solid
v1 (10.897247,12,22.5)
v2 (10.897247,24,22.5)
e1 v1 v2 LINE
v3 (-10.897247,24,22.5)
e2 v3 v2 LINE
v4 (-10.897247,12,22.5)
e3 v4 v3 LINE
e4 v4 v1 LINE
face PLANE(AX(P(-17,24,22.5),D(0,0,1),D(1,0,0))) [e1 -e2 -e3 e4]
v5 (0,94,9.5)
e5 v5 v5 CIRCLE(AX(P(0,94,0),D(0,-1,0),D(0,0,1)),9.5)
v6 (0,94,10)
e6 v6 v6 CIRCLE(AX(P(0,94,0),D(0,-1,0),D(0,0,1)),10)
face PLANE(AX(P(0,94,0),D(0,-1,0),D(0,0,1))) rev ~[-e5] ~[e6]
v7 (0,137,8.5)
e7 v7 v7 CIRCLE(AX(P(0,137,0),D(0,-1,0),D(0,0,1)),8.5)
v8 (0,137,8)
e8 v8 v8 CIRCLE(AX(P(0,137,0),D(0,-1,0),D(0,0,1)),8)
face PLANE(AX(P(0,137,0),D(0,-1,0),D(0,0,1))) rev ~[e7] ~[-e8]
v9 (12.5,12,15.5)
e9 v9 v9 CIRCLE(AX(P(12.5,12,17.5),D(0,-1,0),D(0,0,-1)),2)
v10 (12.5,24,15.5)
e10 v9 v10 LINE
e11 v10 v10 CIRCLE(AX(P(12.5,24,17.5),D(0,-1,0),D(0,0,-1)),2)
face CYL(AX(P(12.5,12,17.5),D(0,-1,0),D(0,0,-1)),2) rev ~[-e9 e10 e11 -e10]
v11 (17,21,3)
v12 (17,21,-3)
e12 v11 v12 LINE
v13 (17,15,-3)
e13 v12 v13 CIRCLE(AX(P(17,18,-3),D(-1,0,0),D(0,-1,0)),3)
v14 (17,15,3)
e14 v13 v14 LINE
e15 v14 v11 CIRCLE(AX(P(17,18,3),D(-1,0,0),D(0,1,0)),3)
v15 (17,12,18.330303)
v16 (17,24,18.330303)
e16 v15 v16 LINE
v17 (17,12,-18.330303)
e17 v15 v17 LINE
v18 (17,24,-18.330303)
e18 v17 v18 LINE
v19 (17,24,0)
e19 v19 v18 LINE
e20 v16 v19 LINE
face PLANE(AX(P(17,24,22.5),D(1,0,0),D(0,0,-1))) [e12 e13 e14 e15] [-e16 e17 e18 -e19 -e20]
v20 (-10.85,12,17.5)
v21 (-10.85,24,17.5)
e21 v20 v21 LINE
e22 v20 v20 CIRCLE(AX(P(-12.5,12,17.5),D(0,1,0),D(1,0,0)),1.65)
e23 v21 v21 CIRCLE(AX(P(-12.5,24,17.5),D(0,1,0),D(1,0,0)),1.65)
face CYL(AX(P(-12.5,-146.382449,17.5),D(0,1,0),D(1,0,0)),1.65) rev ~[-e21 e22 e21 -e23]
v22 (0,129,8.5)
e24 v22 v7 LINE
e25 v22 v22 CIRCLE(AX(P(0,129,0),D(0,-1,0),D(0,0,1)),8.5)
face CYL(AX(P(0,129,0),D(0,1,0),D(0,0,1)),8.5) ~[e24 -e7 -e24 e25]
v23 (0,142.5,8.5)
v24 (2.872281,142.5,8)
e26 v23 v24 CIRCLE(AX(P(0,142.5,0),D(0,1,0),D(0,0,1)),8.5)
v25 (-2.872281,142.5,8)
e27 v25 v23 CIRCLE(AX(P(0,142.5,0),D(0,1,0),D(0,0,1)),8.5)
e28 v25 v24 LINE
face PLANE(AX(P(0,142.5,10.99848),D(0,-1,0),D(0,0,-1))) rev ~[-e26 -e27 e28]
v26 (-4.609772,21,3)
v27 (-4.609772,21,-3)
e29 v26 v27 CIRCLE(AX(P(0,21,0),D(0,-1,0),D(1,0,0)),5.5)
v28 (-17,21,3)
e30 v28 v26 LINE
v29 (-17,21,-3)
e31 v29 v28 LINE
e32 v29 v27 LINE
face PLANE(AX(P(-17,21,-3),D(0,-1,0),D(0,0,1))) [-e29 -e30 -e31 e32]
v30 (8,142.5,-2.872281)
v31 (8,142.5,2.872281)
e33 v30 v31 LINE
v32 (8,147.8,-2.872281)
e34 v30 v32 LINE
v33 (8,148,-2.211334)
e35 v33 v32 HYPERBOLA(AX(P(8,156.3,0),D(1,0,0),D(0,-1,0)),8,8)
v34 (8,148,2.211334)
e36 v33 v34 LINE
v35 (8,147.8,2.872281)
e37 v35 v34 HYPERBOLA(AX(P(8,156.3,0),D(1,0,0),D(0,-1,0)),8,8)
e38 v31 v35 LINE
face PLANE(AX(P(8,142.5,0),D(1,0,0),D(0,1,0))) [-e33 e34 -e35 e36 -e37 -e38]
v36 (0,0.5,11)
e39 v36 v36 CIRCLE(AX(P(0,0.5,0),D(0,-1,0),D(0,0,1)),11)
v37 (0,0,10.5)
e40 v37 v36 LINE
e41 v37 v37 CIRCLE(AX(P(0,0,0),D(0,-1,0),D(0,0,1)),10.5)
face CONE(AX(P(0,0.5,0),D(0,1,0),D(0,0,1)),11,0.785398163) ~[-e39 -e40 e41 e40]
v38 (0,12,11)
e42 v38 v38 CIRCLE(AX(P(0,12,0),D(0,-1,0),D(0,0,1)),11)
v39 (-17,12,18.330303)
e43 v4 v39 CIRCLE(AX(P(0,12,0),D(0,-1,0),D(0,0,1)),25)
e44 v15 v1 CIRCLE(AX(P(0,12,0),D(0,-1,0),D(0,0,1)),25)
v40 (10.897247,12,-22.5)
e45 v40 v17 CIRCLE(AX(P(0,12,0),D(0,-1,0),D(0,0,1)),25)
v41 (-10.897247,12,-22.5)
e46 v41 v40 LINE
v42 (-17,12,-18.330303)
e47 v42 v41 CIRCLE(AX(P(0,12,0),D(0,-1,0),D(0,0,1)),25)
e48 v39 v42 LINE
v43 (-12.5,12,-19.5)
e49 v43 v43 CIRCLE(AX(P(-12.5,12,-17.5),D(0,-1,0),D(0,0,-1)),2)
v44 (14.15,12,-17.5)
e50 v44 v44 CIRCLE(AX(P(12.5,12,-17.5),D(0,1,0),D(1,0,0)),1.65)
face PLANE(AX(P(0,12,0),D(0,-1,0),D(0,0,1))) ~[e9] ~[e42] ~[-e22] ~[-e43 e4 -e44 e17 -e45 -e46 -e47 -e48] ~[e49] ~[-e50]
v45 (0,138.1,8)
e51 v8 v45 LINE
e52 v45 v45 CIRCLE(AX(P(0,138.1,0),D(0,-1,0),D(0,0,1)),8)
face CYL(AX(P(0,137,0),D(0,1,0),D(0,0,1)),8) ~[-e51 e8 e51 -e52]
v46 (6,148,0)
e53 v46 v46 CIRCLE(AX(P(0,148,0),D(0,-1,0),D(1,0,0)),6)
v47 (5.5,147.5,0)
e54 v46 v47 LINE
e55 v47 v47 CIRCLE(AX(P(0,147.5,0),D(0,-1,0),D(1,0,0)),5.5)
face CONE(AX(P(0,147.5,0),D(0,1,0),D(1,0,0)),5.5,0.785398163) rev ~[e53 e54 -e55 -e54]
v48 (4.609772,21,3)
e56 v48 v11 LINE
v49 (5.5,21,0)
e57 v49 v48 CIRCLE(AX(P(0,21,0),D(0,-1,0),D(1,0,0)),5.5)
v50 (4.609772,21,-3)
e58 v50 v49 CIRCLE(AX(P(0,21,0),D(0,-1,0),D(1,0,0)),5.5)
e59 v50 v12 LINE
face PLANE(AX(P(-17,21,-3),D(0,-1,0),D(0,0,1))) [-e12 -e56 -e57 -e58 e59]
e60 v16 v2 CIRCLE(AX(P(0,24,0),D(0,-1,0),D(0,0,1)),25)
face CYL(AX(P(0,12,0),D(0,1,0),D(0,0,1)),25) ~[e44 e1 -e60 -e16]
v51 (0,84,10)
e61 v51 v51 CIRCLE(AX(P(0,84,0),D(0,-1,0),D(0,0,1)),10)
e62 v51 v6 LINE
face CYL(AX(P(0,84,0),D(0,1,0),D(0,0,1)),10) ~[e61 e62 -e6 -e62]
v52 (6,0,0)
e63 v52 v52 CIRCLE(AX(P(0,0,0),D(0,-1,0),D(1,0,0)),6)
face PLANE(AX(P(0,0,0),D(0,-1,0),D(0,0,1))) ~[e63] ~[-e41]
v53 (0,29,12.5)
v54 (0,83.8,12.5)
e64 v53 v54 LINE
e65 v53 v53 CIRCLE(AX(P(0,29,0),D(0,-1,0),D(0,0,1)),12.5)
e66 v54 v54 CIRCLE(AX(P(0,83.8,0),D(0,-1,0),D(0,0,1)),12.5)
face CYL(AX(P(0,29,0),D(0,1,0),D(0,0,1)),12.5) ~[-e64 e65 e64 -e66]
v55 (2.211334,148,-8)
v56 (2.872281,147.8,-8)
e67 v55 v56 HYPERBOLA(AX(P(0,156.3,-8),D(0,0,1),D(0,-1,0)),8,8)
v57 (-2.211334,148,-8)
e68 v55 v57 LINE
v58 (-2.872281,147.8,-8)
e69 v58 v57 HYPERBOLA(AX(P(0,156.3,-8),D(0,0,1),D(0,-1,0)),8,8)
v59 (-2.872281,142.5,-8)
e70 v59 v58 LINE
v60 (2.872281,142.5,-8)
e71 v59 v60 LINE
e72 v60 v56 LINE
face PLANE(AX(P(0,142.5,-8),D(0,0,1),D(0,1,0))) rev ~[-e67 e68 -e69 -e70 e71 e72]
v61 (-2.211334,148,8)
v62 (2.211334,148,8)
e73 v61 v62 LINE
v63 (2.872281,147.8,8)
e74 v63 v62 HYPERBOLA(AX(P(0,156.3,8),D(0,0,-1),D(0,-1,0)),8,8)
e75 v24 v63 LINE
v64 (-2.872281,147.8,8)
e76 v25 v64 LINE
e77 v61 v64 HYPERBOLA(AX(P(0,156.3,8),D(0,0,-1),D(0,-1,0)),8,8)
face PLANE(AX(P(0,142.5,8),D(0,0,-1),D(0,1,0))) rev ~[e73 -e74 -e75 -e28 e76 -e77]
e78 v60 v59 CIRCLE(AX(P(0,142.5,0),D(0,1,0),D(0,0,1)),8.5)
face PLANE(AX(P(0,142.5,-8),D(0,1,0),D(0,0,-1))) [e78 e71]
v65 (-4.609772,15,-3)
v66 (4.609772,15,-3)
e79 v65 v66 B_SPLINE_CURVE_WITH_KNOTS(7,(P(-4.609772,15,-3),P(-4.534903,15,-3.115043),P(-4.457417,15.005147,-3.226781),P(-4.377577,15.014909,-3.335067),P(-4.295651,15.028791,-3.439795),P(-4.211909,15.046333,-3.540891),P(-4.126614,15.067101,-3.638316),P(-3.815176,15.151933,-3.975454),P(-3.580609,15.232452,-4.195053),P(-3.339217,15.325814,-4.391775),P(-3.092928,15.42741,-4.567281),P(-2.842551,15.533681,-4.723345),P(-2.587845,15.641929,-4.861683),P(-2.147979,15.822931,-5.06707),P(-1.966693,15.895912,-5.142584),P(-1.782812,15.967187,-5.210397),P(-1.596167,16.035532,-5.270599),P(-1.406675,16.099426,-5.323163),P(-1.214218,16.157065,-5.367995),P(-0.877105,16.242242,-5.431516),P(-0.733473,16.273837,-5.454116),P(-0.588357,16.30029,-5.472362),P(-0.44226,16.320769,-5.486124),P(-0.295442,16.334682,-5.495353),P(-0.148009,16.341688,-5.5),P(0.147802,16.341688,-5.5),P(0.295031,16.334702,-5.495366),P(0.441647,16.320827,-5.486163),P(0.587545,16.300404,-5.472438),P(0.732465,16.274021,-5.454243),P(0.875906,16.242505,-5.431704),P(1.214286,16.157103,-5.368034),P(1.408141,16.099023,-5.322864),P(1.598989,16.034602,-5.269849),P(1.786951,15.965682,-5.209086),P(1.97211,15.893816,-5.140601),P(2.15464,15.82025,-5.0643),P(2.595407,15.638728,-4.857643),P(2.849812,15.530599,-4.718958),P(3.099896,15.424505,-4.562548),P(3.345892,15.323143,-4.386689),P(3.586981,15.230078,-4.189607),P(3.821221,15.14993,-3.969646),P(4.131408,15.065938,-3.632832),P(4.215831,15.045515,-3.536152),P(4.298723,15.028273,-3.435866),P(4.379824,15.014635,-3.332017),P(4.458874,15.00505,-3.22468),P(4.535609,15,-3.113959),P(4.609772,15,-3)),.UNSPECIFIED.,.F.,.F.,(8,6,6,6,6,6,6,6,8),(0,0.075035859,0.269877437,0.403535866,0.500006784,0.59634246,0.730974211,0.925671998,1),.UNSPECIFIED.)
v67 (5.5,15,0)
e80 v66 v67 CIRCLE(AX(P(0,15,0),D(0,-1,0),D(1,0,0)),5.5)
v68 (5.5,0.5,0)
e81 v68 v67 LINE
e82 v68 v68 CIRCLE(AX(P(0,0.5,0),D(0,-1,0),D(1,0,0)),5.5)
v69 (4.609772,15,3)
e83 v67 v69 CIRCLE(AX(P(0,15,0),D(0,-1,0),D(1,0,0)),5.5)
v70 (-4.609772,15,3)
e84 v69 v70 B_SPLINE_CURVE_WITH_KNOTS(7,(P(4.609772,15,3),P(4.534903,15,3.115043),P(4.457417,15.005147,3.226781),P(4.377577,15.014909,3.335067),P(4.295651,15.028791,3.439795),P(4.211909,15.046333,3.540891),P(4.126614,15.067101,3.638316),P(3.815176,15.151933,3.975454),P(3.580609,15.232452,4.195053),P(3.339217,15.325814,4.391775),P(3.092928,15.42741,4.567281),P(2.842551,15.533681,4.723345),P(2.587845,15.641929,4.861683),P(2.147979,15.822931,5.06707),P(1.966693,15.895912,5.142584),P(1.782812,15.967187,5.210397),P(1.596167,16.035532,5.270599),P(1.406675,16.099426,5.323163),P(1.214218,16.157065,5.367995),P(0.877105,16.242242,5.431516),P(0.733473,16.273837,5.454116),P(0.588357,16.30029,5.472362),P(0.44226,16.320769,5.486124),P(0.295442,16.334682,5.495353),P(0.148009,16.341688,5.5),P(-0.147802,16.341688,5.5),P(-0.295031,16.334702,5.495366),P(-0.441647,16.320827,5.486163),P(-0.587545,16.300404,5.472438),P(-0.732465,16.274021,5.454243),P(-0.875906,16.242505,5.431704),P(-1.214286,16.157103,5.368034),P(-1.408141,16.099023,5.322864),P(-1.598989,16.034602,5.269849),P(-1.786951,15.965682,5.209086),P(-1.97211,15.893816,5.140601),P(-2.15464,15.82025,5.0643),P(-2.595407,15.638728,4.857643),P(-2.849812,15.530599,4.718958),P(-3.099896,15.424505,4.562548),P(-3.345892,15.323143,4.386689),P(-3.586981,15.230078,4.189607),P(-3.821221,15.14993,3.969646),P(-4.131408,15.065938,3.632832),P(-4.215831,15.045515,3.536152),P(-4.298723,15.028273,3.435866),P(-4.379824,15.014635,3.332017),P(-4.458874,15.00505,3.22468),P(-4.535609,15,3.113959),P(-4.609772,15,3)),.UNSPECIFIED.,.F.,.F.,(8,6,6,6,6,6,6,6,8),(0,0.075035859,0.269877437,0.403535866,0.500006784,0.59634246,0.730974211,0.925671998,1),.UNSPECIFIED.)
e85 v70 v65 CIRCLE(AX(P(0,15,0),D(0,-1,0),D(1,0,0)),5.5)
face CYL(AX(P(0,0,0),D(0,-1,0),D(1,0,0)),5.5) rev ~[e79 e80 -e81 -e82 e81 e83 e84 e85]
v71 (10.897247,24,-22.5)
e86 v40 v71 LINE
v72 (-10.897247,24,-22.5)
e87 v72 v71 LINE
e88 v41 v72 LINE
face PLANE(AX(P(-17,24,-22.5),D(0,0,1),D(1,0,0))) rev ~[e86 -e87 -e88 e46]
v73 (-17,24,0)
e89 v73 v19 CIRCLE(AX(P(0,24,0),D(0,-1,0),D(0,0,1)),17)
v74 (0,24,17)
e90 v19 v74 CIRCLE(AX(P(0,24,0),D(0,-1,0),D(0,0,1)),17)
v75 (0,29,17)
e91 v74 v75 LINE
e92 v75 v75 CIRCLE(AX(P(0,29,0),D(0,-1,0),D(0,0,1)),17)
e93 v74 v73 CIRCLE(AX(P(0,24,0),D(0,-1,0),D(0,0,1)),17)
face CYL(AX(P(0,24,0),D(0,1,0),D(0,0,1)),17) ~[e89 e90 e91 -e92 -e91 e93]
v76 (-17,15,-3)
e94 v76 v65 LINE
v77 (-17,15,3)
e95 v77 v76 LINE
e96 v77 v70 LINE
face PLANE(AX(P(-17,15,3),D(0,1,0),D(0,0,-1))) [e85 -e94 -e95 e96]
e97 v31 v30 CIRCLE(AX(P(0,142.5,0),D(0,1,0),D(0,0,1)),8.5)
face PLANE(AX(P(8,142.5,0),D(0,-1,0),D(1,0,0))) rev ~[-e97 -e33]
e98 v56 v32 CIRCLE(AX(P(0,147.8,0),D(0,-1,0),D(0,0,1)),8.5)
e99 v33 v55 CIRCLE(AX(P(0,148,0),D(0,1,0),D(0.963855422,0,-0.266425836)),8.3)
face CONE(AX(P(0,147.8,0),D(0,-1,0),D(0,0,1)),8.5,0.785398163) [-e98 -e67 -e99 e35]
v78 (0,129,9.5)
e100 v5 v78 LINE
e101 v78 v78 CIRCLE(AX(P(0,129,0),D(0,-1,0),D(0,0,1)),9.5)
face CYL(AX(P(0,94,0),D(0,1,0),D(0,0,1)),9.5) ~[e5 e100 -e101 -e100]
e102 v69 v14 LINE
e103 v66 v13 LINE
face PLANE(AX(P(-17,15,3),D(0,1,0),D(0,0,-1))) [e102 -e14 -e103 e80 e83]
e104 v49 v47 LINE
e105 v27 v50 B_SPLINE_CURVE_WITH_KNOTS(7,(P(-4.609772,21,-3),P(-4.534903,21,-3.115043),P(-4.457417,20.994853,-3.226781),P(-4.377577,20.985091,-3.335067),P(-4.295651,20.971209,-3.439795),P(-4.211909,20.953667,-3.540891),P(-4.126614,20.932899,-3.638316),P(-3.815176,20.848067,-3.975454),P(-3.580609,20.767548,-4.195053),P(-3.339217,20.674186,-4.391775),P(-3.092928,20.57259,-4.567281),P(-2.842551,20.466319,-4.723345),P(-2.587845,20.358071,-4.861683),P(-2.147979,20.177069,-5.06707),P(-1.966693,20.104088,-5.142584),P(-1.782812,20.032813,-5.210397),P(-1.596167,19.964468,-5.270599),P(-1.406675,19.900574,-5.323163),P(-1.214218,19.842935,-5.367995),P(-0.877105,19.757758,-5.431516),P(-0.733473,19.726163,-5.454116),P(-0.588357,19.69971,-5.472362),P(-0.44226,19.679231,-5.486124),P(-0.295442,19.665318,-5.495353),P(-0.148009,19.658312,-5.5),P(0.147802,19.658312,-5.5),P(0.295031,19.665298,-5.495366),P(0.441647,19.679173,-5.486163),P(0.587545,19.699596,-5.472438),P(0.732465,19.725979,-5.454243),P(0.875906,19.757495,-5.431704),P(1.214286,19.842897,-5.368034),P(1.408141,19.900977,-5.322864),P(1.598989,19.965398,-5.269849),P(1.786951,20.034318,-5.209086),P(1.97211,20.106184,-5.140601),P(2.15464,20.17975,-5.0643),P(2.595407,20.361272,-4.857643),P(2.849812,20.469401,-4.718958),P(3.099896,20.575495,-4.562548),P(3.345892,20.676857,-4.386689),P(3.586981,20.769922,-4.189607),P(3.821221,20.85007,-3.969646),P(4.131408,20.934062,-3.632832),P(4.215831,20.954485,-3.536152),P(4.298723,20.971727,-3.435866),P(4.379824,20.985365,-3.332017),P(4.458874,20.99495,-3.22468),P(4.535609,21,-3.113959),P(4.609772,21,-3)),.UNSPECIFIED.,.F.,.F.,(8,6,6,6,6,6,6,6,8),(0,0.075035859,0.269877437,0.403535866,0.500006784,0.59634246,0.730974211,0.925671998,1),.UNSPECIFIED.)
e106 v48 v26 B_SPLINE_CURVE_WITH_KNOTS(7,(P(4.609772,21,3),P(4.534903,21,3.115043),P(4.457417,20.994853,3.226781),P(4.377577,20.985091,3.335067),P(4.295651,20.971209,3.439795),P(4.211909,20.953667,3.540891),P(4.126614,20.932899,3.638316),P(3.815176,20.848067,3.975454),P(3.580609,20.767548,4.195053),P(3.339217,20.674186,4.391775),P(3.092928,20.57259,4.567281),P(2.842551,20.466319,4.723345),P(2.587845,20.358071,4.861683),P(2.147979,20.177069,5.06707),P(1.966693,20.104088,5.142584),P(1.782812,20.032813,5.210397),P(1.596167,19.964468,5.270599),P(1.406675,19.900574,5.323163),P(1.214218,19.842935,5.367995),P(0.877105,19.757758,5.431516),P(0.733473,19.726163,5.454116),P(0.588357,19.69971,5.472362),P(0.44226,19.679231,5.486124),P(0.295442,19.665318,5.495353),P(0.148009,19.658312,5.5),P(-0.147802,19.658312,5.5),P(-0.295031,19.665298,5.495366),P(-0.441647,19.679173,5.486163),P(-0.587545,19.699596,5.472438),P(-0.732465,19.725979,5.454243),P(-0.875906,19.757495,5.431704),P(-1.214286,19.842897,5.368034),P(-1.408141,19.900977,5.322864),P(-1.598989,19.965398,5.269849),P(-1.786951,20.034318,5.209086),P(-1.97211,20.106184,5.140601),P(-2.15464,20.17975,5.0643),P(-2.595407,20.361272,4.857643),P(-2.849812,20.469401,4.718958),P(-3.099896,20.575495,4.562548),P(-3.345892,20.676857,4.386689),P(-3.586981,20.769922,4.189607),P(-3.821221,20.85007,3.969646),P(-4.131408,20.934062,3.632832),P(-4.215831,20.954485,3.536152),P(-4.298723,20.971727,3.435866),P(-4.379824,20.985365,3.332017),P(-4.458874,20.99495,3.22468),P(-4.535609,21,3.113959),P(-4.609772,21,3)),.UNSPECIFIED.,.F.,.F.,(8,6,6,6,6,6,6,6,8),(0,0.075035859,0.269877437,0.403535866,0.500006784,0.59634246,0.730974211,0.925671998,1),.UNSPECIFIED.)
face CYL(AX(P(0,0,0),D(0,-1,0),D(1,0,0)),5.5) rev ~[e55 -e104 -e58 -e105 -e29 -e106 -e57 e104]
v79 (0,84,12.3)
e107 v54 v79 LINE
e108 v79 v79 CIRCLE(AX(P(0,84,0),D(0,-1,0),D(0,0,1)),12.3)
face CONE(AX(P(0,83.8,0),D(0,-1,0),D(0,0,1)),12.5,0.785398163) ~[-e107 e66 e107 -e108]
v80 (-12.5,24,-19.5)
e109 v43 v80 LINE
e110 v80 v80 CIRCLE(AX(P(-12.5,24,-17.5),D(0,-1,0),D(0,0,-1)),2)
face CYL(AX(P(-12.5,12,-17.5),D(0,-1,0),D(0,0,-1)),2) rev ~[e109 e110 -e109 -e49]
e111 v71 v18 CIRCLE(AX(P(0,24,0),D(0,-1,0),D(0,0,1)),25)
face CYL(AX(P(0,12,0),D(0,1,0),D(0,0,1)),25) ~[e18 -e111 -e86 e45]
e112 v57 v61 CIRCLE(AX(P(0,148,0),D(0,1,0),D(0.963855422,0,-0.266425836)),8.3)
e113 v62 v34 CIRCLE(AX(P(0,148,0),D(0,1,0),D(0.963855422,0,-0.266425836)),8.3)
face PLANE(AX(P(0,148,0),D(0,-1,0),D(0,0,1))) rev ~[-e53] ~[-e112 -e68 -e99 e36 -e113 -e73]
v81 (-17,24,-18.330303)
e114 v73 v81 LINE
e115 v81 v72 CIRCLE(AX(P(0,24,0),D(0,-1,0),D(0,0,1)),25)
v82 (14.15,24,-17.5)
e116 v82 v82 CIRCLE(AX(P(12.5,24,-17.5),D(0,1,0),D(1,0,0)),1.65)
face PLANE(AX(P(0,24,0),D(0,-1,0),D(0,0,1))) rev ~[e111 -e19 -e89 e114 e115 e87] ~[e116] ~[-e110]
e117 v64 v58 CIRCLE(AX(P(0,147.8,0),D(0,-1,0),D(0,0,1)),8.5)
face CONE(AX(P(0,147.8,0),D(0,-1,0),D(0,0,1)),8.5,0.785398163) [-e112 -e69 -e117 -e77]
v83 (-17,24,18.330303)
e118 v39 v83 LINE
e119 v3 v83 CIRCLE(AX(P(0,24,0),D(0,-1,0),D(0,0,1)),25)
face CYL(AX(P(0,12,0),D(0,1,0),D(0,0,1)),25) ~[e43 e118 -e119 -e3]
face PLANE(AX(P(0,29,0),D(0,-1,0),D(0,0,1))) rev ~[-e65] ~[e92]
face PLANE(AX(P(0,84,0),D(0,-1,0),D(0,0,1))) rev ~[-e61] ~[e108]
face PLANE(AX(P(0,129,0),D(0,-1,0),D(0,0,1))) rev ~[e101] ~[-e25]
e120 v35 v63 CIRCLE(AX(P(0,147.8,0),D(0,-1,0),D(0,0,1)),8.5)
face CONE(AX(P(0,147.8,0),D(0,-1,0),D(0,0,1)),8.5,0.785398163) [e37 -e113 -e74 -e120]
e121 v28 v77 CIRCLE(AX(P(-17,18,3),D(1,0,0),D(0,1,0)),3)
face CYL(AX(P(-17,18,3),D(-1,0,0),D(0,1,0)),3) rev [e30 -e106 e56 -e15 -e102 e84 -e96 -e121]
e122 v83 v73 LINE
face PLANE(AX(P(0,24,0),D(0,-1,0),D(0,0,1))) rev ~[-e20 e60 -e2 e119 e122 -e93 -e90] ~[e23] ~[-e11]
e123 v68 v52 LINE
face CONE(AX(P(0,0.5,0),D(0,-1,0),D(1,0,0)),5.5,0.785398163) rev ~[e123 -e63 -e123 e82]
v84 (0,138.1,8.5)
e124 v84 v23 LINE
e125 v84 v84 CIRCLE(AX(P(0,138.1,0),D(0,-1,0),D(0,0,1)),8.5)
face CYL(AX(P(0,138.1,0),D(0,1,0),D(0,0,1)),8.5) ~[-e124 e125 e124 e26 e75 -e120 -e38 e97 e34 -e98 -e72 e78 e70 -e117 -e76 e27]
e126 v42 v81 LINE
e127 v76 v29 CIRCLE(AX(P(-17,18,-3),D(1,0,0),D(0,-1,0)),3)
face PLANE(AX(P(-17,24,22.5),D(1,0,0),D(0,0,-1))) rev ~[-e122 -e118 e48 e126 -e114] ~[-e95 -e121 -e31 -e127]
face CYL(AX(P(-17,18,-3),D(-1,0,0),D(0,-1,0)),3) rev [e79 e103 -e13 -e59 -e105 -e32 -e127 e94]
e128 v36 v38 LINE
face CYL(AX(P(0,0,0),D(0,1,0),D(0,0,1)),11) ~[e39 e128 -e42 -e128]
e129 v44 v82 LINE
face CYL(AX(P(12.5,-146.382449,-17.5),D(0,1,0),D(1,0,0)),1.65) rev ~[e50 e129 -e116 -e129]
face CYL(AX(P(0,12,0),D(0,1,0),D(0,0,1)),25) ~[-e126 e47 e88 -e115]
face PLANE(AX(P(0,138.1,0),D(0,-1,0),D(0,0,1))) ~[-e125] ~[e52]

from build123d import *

# Parameters (mm, degrees)
SKETCH7_OUTSIDE_W   = 84.804
SKETCH7_OUTSIDE_H   = 84.804
SKETCH7_OUTSIDE_W_2 = 34
SKETCH7_OUTSIDE_H_2 = 45
CUT_EXTRUDE3_DEPTH  = 25
M4_TAPPED_HOLE2_D   = 3.3
SKETCH13_R          = 2
CUT_EXTRUDE6_DEPTH  = 25
SKETCH14_R          = 5.5
CUT_EXTRUDE7_DEPTH  = 151.66270275
CHAMFER1_SIZE       = 0.2
CHAMFER2_SIZE       = 0.5
SKETCH15_W          = 4.842021814
SKETCH15_H          = 7.203372967
CUT_EXTRUDE8_DEPTH  = 5
CUT_EXTRUDE9_DEPTH  = 154.513028763
SKETCH17_W          = 3.088959923
SKETCH17_H          = 8.04850145
SKETCH17_W_2        = 2.99848013
SKETCH17_H_2        = 8.967280155
CUT_EXTRUDE10_DEPTH = 5


with BuildPart() as part:
    # Sketch1 → Revolve1 (revolve)
    with BuildSketch(Plane.XY, mode=Mode.PRIVATE) as revolve1_sk:
        Polygon((0, 0), (11, 0), (11, 12), (25, 12), (25, 24), (17, 24), (17, 29), (12.5, 29), (12.5, 84), (10, 84), (10, 94), (9.5, 94), (9.5, 129), (8.5, 129), (8.5, 137), (8, 137), (8, 138.1), (8.5, 138.1), (8.5, 148), (0, 148), align=None)
    revolve(revolve1_sk.sketch.rotate(Axis((0, 148, 0), (0, -1, 0)), 90), axis=Axis((0, 148, 0), (0, -1, 0)))

    # Sketch7 outside → Cut-Extrude3 (cut)
    with BuildSketch(Plane(origin=(0, 24, 0), x_dir=(1, 0, 0), z_dir=(0, 1, 0))):
        Rectangle(SKETCH7_OUTSIDE_W, SKETCH7_OUTSIDE_H)
        Rectangle(SKETCH7_OUTSIDE_W_2, SKETCH7_OUTSIDE_H_2, mode=Mode.SUBTRACT)
    extrude(amount=-CUT_EXTRUDE3_DEPTH, mode=Mode.SUBTRACT)

    # M4 Tapped Hole2 (through all)
    with Locations(Plane(origin=(0, 12, 0), x_dir=(-1, 0, 0), z_dir=(0, -1, 0))):
        with Locations((-12.5, 17.5), (12.5, -17.5)):
            Hole(M4_TAPPED_HOLE2_D / 2)

    # Sketch13 → Cut-Extrude6 (cut)
    with BuildSketch(Plane.XZ.offset(-12)):
        with Locations(Location((12.5, 17.5, 0), (0, 0, 270))):
            Circle(SKETCH13_R)
        with Locations(Location((-12.5, -17.5, 0), (0, 0, 270))):
            Circle(SKETCH13_R)
    extrude(amount=-CUT_EXTRUDE6_DEPTH, mode=Mode.SUBTRACT)

    # Sketch14 → Cut-Extrude7 (cut, through all)
    with BuildSketch(Plane.XZ):
        Circle(SKETCH14_R)
    extrude(amount=-CUT_EXTRUDE7_DEPTH, mode=Mode.SUBTRACT)

    # Chamfer1
    chamfer1_edges = [part.edges().sort_by_distance(p)[0] for p in [
        (0, 148, -8.5),
        (0, 84, -12.5),
    ]]
    chamfer(chamfer1_edges, length=CHAMFER1_SIZE)

    # Chamfer2
    chamfer2_edges = [part.edges().sort_by_distance(p)[0] for p in [
        (-5.5, 148, 0),
        (-5.5, 0, 0),
        (0, 0, -11),
    ]]
    chamfer(chamfer2_edges, length=CHAMFER2_SIZE)

    # Sketch15 → Cut-Extrude8 (cut, symmetric)
    with BuildSketch(Plane.XY):
        with Locations((10.421010907, 146.101686484)):
            Rectangle(SKETCH15_W, SKETCH15_H)
    extrude(amount=CUT_EXTRUDE8_DEPTH, both=True, mode=Mode.SUBTRACT)

    # Sketch16 → Cut-Extrude9 (cut, through all)
    with BuildSketch(Plane.ZY.offset(17)):
        with BuildLine():
            Line((-3, 21), (3, 21))
            ThreePointArc((3, 21), (6, 18), (3, 15))
            Line((3, 15), (-3, 15))
            ThreePointArc((-3, 15), (-6, 18), (-3, 21))
        make_face()
    extrude(amount=-CUT_EXTRUDE9_DEPTH, mode=Mode.SUBTRACT)

    # Sketch17 → Cut-Extrude10 (cut, symmetric)
    with BuildSketch(Plane(origin=(0, 0, 0), x_dir=(0, 0, -1), z_dir=(1, 0, 0))):
        with Locations((9.544479962, 146.524250725)):
            Rectangle(SKETCH17_W, SKETCH17_H)
        with Locations((-9.499240065, 146.983640078)):
            Rectangle(SKETCH17_W_2, SKETCH17_H_2)
    extrude(amount=CUT_EXTRUDE10_DEPTH, both=True, mode=Mode.SUBTRACT)


solid = part.part
